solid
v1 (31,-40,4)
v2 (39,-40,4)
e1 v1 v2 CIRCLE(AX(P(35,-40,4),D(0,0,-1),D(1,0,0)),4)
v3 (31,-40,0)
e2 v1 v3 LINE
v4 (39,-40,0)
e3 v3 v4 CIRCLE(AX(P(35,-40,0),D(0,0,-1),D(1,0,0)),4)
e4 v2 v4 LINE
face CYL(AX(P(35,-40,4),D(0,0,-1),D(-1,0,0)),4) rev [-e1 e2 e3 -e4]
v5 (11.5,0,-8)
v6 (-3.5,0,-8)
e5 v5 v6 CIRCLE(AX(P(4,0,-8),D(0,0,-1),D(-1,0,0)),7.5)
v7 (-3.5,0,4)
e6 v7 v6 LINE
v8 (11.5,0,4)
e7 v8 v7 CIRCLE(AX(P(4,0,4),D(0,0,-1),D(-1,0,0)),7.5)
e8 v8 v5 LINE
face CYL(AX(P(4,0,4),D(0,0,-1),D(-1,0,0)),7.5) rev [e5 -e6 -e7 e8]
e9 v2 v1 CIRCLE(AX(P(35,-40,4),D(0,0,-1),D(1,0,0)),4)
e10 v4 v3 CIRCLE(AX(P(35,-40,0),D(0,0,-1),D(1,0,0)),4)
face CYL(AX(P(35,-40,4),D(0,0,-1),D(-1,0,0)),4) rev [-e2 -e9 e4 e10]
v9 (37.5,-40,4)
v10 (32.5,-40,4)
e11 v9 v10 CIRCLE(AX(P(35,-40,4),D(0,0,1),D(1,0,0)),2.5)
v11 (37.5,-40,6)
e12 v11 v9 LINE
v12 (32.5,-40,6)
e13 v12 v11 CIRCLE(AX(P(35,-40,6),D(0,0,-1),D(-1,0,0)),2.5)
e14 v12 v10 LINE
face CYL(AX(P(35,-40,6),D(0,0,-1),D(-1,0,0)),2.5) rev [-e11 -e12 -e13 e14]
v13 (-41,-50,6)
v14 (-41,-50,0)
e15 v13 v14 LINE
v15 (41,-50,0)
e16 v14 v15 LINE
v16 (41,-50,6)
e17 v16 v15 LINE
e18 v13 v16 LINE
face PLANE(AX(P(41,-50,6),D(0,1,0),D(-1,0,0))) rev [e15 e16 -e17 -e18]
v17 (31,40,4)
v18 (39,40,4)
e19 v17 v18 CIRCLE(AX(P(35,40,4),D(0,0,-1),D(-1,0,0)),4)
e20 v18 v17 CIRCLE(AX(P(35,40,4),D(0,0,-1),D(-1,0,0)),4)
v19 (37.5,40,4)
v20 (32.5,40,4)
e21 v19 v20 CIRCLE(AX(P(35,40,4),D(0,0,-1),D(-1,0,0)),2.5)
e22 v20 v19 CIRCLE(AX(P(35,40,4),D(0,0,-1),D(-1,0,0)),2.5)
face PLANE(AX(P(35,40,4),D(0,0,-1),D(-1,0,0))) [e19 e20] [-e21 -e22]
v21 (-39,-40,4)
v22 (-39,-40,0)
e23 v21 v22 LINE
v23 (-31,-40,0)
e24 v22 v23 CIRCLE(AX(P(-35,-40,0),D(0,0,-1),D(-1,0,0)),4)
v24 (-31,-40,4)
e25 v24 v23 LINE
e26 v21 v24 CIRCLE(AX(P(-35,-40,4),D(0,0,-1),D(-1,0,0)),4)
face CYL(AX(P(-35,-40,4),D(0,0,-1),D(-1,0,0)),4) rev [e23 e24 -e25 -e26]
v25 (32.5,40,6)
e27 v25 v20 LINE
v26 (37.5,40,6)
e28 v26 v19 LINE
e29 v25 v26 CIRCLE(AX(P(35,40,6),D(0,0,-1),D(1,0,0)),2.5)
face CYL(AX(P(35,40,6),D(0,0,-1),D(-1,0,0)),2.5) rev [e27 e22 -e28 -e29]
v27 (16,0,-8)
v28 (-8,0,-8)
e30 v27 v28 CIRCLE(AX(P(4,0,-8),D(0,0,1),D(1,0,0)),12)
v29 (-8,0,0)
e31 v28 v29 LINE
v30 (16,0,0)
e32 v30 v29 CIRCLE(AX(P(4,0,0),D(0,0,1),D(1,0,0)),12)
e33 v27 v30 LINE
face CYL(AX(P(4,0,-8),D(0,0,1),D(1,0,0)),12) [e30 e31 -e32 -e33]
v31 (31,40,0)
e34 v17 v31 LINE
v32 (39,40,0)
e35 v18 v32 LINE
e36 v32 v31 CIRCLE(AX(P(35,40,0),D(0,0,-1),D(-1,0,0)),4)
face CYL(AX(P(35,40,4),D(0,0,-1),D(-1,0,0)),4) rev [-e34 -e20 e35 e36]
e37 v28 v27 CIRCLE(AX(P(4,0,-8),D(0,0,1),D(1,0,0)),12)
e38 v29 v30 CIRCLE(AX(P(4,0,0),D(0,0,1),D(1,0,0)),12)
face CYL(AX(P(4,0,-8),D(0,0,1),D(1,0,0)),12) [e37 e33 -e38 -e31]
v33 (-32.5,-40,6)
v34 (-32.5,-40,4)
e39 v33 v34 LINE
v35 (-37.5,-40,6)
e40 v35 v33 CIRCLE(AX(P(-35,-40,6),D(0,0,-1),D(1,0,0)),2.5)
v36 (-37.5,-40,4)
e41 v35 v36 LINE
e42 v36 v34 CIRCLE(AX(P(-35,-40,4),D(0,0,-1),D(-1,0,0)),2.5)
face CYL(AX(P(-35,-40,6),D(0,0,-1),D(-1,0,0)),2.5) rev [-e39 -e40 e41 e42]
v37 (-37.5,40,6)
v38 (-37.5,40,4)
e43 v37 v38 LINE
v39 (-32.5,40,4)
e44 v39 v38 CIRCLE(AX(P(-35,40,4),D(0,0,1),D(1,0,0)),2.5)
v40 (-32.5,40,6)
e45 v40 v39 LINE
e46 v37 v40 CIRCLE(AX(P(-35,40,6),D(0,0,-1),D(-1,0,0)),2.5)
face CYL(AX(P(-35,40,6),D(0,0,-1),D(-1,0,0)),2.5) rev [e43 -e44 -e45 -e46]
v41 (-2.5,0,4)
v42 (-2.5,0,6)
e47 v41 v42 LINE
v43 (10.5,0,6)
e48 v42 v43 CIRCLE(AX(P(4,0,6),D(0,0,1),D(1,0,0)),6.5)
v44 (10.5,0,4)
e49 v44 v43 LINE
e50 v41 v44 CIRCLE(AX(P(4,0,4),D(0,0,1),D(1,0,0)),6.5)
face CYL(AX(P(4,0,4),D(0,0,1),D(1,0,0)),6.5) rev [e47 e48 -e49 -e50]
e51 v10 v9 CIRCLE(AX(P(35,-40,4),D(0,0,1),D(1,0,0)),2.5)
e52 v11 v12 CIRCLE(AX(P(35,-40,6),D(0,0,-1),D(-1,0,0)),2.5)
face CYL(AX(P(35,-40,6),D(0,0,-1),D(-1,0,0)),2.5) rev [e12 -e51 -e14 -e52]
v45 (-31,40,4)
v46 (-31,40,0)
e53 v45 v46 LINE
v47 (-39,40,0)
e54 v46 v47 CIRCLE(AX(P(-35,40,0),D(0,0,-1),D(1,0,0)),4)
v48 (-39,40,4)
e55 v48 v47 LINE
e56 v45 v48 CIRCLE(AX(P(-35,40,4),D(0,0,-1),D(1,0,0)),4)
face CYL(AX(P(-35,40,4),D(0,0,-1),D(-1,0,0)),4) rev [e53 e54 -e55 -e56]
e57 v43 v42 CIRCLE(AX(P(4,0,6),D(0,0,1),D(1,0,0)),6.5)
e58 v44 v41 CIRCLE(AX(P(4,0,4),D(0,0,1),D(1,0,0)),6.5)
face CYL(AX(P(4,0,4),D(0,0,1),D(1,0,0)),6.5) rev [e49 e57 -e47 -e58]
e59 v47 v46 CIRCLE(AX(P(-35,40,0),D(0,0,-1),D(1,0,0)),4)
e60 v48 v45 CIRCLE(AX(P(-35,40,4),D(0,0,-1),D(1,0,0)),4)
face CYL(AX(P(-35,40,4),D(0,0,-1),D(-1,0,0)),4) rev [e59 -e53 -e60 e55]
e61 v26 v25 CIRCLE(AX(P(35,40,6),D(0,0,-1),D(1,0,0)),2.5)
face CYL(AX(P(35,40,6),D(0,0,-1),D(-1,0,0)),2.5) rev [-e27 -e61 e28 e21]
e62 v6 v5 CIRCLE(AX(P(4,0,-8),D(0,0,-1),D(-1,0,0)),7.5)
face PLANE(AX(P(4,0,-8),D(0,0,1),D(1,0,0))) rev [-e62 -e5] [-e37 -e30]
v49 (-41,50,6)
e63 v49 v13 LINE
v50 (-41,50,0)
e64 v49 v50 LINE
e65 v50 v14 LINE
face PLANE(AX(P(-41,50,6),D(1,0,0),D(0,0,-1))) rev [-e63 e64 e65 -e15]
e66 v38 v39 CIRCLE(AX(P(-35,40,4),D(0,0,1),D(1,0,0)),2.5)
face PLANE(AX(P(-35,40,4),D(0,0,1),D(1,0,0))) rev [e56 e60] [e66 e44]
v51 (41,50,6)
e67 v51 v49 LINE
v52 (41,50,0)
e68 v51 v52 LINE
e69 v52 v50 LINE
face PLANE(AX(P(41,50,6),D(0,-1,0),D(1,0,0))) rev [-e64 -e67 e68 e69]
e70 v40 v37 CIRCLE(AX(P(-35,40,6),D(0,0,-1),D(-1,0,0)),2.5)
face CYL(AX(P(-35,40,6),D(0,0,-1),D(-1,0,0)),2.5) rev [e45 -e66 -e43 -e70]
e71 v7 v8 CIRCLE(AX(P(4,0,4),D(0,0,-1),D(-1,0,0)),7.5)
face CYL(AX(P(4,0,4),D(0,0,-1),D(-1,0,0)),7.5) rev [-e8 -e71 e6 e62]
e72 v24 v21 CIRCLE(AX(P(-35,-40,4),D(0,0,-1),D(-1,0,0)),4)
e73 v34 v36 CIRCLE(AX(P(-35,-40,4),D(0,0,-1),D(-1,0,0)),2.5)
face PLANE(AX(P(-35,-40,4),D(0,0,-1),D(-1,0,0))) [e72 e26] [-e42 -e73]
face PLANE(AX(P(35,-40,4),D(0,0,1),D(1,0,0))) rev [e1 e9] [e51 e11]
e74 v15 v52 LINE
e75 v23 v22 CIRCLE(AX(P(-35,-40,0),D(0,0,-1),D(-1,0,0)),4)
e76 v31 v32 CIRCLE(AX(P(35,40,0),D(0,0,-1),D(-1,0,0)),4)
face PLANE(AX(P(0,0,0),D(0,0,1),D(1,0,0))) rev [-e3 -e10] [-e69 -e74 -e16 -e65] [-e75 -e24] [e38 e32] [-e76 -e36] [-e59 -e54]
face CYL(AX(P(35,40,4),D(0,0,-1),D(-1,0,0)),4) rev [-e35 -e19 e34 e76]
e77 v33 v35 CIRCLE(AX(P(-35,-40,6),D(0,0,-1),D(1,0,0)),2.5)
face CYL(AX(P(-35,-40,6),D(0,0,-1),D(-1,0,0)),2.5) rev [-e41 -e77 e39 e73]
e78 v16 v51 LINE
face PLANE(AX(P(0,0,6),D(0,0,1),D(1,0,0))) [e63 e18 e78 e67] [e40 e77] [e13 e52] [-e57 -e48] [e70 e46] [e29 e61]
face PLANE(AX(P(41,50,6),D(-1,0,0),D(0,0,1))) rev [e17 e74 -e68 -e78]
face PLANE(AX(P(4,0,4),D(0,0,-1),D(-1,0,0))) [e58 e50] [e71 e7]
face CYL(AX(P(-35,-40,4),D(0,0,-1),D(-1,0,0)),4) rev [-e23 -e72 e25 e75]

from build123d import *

# Parameters (mm, degrees)
SKETCH_1_W           = 82
SKETCH_1_H           = 100
EXTRUDE_1_DEPTH      = 6
SKETCH_3_R           = 12
EXTRUDE_3_DEPTH      = 14
SKETCH_7_R           = 4
CUT_EXTRUDE_4_DEPTH  = 4
SKETCH_5_R           = 6.5
CUT_EXTRUDE_8_DEPTH  = 2
SKETCH_11_R          = 7.5
CUT_EXTRUDE_9_DEPTH  = 12
SKETCH_12_R          = 2.5
CUT_EXTRUDE_10_DEPTH = 6


with BuildPart() as part:
    # 草图1 → 凸台-拉伸1 (new body)
    with BuildSketch(Plane.XY):
        Rectangle(SKETCH_1_W, SKETCH_1_H)
    extrude(amount=EXTRUDE_1_DEPTH)

    # 草图3 → 凸台-拉伸3 (add)
    with BuildSketch(Plane.XY.offset(6)):
        with Locations((4, 0)):
            Circle(SKETCH_3_R)
    extrude(amount=-EXTRUDE_3_DEPTH)

    # 草图7 → 切除-拉伸4 (cut)
    with BuildSketch(Plane(origin=(0, 0, 0), x_dir=(-1, 0, 0), z_dir=(0, 0, -1))):
        with Locations((-35, 40)):
            Circle(SKETCH_7_R)
        with Locations(Location((-35, -40, 0), (0, 0, 180))):
            Circle(SKETCH_7_R)
        with Locations((35, -40)):
            Circle(SKETCH_7_R)
        with Locations(Location((35, 40, 0), (0, 0, 180))):
            Circle(SKETCH_7_R)
    extrude(amount=-CUT_EXTRUDE_4_DEPTH, mode=Mode.SUBTRACT)

    # 草图5 → 切除-拉伸8 (cut)
    with BuildSketch(Plane.XY.offset(6)):
        with Locations((4, 0)):
            Circle(SKETCH_5_R)
    extrude(amount=-CUT_EXTRUDE_8_DEPTH, mode=Mode.SUBTRACT)

    # 草图11 → 切除-拉伸9 (cut)
    with BuildSketch(Plane(origin=(0, 0, -8), x_dir=(-1, 0, 0), z_dir=(0, 0, -1))):
        with Locations((-4, 0)):
            Circle(SKETCH_11_R)
    extrude(amount=-CUT_EXTRUDE_9_DEPTH, mode=Mode.SUBTRACT)

    # 草图12 → 切除-拉伸10 (cut)
    with BuildSketch(Plane(origin=(0, 0, 0), x_dir=(-1, 0, 0), z_dir=(0, 0, -1))):
        with Locations((-35, -40)):
            Circle(SKETCH_12_R)
        with Locations((-35, 40)):
            Circle(SKETCH_12_R)
        with Locations((35, -40)):
            Circle(SKETCH_12_R)
        with Locations((35, 40)):
            Circle(SKETCH_12_R)
    extrude(amount=-CUT_EXTRUDE_10_DEPTH, mode=Mode.SUBTRACT)


solid = part.part
